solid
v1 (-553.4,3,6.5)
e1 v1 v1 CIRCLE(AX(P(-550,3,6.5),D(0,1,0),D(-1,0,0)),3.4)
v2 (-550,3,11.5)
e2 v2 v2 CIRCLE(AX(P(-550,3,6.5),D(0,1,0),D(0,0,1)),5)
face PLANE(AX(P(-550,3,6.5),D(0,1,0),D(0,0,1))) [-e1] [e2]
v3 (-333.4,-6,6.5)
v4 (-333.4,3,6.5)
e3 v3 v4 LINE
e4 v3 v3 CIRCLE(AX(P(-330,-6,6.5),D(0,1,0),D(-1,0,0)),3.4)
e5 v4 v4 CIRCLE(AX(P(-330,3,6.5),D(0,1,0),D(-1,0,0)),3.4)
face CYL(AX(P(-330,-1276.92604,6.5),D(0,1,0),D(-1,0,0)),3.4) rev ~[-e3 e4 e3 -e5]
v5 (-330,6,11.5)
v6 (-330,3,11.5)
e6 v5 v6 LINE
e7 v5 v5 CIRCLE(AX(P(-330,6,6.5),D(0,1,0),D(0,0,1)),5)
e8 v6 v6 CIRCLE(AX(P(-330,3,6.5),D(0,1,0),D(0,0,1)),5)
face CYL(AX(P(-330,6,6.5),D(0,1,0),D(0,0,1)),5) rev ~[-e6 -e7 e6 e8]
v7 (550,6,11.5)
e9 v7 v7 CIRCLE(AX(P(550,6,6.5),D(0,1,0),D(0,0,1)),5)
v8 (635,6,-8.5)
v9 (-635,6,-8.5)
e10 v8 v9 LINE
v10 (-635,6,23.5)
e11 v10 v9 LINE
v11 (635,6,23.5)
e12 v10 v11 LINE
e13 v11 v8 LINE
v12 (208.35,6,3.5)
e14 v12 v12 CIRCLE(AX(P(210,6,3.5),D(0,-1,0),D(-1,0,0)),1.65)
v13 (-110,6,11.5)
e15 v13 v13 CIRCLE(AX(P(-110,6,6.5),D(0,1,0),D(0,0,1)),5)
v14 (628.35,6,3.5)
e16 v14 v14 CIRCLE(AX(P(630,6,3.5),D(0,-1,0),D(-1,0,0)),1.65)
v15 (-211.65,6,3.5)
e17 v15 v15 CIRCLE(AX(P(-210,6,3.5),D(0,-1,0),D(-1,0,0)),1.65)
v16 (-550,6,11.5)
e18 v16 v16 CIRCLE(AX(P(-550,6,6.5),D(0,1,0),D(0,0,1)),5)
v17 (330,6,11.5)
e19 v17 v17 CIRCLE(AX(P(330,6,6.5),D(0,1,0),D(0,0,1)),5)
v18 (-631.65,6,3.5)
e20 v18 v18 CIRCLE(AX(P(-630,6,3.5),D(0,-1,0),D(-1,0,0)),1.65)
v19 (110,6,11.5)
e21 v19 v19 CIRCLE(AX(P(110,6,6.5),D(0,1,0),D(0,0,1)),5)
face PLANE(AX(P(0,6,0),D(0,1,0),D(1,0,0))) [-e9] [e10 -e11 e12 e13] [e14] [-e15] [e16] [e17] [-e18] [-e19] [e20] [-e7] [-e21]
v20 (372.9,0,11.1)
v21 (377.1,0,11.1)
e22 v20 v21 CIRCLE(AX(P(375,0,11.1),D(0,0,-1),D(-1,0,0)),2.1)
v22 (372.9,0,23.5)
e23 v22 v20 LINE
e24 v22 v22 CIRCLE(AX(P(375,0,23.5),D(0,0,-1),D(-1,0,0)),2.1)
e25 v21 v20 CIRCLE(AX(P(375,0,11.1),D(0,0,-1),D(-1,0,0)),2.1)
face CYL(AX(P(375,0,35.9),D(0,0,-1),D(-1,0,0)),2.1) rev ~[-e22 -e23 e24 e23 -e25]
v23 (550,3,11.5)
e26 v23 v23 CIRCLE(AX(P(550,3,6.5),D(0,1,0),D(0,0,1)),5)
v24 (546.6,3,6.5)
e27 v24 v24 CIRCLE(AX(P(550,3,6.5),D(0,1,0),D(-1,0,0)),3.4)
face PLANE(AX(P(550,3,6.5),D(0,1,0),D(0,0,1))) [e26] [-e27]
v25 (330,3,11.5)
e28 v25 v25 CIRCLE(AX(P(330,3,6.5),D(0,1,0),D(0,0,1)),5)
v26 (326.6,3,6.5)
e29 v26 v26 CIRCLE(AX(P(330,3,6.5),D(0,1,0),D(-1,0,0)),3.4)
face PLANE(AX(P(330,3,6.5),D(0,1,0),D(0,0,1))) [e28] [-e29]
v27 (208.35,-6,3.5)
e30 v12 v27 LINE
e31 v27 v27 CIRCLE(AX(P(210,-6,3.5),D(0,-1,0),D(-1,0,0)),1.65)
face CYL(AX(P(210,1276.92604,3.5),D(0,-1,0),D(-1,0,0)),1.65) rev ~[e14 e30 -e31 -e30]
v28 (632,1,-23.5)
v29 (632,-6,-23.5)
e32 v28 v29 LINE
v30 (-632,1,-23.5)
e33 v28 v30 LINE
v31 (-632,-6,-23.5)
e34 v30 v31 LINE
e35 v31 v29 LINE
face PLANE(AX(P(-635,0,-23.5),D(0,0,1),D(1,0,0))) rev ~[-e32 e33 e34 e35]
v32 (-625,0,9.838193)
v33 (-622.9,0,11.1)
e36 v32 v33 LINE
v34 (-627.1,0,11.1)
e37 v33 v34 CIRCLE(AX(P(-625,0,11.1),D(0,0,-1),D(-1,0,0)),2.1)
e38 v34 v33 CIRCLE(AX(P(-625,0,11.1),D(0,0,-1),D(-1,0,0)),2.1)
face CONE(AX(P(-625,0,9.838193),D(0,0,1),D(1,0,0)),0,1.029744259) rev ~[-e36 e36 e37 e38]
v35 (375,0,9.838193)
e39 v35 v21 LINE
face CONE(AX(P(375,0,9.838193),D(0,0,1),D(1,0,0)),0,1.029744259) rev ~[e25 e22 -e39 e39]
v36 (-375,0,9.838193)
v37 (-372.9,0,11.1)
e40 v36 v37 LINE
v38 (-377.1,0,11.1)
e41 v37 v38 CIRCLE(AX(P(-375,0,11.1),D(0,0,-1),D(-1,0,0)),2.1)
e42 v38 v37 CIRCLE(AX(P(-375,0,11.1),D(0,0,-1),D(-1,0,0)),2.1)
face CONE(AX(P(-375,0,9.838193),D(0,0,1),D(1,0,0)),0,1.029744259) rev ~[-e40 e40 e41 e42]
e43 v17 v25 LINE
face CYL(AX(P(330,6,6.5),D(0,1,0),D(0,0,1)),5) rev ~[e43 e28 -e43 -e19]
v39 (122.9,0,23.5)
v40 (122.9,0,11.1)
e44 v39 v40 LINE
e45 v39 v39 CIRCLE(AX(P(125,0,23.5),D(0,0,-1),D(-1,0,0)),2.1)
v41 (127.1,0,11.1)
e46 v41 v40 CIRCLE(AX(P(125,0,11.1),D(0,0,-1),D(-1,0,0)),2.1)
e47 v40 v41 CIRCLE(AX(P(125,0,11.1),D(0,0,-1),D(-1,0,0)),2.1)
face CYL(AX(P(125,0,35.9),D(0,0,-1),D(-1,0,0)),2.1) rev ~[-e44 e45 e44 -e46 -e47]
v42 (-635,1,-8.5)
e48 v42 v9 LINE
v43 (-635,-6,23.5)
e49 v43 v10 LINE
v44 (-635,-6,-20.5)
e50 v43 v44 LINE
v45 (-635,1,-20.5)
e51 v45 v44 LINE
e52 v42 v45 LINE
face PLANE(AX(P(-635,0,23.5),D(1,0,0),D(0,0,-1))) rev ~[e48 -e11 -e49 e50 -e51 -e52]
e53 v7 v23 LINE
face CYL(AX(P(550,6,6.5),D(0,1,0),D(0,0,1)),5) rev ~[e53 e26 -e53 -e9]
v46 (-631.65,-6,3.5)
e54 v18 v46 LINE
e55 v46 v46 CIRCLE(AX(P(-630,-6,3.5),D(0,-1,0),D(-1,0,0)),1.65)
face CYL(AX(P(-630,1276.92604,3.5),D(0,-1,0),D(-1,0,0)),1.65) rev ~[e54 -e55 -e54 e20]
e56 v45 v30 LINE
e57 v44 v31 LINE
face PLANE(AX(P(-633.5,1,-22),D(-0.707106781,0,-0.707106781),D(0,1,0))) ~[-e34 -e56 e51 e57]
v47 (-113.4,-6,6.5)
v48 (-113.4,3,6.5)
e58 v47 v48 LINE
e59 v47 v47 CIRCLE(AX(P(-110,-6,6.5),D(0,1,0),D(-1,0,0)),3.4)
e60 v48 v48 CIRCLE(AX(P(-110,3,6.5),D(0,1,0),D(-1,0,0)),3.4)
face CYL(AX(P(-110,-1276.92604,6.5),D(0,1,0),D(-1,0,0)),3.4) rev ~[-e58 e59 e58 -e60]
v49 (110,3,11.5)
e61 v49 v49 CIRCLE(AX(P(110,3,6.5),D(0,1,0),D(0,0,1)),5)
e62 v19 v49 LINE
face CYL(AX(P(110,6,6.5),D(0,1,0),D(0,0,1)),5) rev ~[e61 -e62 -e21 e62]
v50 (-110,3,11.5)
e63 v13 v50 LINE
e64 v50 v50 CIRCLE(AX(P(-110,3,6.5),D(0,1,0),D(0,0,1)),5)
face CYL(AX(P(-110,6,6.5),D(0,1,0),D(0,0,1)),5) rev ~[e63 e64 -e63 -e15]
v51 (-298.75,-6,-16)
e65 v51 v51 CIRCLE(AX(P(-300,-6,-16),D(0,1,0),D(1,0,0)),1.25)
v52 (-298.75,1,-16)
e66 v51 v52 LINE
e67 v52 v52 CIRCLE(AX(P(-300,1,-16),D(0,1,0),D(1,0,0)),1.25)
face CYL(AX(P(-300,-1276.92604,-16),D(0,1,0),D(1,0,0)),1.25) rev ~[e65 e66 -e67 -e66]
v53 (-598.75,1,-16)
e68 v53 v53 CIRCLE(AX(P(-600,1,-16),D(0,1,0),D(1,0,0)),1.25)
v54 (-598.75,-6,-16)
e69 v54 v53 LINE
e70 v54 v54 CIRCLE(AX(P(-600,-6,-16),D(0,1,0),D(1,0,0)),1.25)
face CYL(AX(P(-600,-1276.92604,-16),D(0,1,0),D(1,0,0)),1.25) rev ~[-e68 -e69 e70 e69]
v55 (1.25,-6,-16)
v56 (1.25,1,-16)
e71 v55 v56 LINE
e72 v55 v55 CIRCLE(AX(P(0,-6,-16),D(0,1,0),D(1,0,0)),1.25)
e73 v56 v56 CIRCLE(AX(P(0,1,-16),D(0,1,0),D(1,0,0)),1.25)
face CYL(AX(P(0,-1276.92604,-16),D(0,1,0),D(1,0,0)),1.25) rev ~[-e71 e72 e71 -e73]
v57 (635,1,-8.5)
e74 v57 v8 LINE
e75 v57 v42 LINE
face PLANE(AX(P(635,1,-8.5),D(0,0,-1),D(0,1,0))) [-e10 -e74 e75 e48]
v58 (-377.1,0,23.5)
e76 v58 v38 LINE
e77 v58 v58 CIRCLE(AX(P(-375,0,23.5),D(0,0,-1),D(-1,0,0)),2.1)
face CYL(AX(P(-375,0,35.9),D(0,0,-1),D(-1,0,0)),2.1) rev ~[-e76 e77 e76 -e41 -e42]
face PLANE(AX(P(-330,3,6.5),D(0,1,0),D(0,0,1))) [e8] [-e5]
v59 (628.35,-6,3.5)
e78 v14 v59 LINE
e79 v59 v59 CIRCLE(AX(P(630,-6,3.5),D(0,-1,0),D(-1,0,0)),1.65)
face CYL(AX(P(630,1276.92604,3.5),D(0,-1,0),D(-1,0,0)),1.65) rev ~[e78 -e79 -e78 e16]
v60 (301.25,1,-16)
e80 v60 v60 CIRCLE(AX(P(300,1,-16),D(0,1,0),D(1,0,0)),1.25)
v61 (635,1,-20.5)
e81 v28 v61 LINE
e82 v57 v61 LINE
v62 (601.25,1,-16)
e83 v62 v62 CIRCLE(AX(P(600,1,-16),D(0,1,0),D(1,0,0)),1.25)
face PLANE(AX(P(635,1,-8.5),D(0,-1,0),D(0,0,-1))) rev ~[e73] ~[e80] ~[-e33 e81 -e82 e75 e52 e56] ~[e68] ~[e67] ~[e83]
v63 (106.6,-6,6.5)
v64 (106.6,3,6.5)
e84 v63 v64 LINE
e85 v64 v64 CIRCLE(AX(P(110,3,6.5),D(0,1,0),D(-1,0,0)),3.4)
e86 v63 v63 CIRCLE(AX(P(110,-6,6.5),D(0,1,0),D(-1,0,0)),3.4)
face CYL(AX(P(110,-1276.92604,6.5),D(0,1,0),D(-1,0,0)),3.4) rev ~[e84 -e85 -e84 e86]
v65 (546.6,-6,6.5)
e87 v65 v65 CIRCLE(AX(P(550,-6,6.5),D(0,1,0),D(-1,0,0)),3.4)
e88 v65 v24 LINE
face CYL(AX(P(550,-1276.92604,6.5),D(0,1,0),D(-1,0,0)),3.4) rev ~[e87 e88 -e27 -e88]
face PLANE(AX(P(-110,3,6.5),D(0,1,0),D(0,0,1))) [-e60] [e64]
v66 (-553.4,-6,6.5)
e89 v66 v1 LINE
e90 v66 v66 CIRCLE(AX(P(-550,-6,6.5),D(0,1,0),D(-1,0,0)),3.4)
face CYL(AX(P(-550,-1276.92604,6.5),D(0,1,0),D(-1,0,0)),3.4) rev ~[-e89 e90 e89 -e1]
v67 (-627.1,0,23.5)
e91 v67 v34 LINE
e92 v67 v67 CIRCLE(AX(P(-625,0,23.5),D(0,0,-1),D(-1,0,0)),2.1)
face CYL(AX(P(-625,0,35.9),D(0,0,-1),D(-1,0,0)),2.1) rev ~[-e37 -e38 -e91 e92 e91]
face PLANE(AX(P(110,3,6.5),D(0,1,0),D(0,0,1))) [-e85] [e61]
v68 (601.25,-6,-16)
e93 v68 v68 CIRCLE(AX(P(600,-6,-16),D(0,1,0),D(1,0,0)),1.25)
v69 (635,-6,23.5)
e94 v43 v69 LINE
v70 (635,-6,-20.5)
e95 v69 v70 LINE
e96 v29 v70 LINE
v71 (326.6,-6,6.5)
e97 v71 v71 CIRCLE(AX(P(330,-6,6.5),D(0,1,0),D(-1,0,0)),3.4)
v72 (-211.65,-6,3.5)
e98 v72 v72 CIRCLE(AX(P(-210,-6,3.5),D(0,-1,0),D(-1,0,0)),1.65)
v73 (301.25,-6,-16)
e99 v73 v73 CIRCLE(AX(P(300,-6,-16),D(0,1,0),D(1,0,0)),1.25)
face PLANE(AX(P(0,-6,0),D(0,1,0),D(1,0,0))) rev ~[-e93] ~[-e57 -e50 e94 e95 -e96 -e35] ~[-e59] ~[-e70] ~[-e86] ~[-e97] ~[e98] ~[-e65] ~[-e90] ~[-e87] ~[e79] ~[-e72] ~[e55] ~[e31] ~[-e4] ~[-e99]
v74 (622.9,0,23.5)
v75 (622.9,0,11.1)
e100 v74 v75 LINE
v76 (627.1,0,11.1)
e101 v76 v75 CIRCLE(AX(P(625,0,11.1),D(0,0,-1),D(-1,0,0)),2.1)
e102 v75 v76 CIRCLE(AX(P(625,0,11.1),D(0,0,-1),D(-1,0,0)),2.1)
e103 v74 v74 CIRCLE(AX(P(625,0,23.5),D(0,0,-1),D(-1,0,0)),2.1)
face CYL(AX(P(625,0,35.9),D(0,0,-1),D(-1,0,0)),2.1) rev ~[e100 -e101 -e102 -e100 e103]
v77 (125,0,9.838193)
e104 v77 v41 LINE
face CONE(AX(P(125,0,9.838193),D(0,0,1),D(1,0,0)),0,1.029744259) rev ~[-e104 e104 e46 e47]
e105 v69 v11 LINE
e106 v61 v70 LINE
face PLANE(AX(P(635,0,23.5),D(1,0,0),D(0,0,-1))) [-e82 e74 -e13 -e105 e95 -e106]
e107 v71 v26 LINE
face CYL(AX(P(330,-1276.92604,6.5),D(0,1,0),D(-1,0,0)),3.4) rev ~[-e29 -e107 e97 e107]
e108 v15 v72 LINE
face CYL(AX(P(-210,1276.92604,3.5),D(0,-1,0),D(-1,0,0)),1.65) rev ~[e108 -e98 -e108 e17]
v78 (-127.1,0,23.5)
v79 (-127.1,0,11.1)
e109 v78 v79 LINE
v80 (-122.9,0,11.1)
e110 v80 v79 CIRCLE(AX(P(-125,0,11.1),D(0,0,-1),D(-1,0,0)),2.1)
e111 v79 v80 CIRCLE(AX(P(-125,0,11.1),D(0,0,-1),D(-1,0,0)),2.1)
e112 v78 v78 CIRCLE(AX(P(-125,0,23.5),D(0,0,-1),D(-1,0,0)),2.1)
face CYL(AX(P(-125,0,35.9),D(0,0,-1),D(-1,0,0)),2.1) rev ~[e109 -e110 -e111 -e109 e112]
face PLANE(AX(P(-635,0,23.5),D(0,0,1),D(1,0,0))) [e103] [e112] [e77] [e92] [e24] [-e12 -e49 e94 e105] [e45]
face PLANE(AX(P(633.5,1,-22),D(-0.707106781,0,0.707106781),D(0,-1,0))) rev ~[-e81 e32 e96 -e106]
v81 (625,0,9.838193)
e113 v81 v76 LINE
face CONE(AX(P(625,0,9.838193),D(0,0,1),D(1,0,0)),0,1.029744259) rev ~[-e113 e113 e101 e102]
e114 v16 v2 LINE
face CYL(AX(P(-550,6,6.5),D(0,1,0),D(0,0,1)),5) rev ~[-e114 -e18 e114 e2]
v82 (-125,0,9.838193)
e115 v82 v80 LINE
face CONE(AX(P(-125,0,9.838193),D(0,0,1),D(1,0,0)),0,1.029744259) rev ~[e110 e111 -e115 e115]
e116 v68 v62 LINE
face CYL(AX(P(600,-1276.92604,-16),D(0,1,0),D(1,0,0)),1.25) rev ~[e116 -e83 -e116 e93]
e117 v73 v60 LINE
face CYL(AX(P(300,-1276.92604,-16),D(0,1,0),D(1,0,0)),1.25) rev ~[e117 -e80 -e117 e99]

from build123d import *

# Parameters (mm, degrees)
SKETCH_1_W             = 1270
SKETCH_1_H             = 47
EXTRUDE_1_DEPTH        = 6
SKETCH_2_W             = 15
SKETCH_2_H             = 5
CUT_EXTRUDE_1_DEPTH    = 1271.231573376
CHAMFER_1_SIZE         = 3
HOLE_WIZARD_M5_1_D     = 4.2
HOLE_WIZARD_M5_1_DEPTH = 12.4
HOLE_WIZARD_M5_1_TIP   = 1.2618073
HOLE_WIZARD_M4_1_D     = 3.3
HOLE_WIZARD_M3_1_D     = 2.5
HOLE_WIZARD_M8_1_D     = 6.8
SKETCH_12_R            = 5
CUT_EXTRUDE_2_DEPTH    = 3


with BuildPart() as part:
    # 草图1 → 凸台-拉伸1 (new, symmetric)
    with BuildSketch(Plane(origin=(0, 0, 0), x_dir=(1, 0, 0), z_dir=(0, 1, 0))):
        Rectangle(SKETCH_1_W, SKETCH_1_H)
    extrude(amount=EXTRUDE_1_DEPTH, both=True)

    # 草图2 → 切除-拉伸1 (cut, through all)
    with BuildSketch(Plane(origin=(635, 0, 0), x_dir=(0, 0, -1), z_dir=(1, 0, 0))):
        with Locations((16, 3.5)):
            Rectangle(SKETCH_2_W, SKETCH_2_H)
    extrude(amount=-CUT_EXTRUDE_1_DEPTH, mode=Mode.SUBTRACT)

    # 倒角1
    chamfer_1_edges = [part.edges().sort_by_distance(p)[0] for p in [
        (-635, -2.5, -23.5),
        (635, -2.5, -23.5),
    ]]
    chamfer(chamfer_1_edges, length=CHAMFER_1_SIZE)

    # M5 螺纹孔1
    with Locations(Plane.XY.offset(23.5)):
        with Locations((-625, 0), (-375, 0), (-125, 0), (125, 0), (375, 0), (625, 0)):
            Hole(HOLE_WIZARD_M5_1_D / 2, depth=HOLE_WIZARD_M5_1_DEPTH)
            with Locations((0, 0, -(HOLE_WIZARD_M5_1_DEPTH + HOLE_WIZARD_M5_1_TIP / 2))):  # 118° drill point
                Cone(0, HOLE_WIZARD_M5_1_D / 2, HOLE_WIZARD_M5_1_TIP, mode=Mode.SUBTRACT)

    # M4 螺纹孔1 (through all)
    with Locations(Plane(origin=(0, 6, 0), x_dir=(1, 0, 0), z_dir=(0, 1, 0))):
        with Locations((630, -3.5), (-630, -3.5), (210, -3.5), (-210, -3.5)):
            Hole(HOLE_WIZARD_M4_1_D / 2)

    # M3 螺纹孔1 (through all)
    with Locations(Plane(origin=(0, -6, 0), x_dir=(-1, 0, 0), z_dir=(0, -1, 0))):
        with Locations((-600, 16), (-300, 16), (0, 16), (300, 16), (600, 16)):
            Hole(HOLE_WIZARD_M3_1_D / 2)

    # M8 螺纹孔1 (through all)
    with Locations(Plane.XZ.offset(6)):
        with Locations((550, 6.5), (330, 6.5), (110, 6.5), (-110, 6.5), (-330, 6.5), (-550, 6.5)):
            Hole(HOLE_WIZARD_M8_1_D / 2)

    # 草图12 → 切除-拉伸2 (cut)
    with BuildSketch(Plane(origin=(0, 6, 0), x_dir=(1, 0, 0), z_dir=(0, 1, 0))):
        with Locations(Location((550, -6.5, 0), (0, 0, 270))):
            Circle(SKETCH_12_R)
        with Locations(Location((330, -6.5, 0), (0, 0, 270))):
            Circle(SKETCH_12_R)
        with Locations(Location((110, -6.5, 0), (0, 0, 270))):
            Circle(SKETCH_12_R)
        with Locations(Location((-110, -6.5, 0), (0, 0, 270))):
            Circle(SKETCH_12_R)
        with Locations(Location((-330, -6.5, 0), (0, 0, 270))):
            Circle(SKETCH_12_R)
        with Locations(Location((-550, -6.5, 0), (0, 0, 270))):
            Circle(SKETCH_12_R)
    extrude(amount=-CUT_EXTRUDE_2_DEPTH, mode=Mode.SUBTRACT)


solid = part.part
